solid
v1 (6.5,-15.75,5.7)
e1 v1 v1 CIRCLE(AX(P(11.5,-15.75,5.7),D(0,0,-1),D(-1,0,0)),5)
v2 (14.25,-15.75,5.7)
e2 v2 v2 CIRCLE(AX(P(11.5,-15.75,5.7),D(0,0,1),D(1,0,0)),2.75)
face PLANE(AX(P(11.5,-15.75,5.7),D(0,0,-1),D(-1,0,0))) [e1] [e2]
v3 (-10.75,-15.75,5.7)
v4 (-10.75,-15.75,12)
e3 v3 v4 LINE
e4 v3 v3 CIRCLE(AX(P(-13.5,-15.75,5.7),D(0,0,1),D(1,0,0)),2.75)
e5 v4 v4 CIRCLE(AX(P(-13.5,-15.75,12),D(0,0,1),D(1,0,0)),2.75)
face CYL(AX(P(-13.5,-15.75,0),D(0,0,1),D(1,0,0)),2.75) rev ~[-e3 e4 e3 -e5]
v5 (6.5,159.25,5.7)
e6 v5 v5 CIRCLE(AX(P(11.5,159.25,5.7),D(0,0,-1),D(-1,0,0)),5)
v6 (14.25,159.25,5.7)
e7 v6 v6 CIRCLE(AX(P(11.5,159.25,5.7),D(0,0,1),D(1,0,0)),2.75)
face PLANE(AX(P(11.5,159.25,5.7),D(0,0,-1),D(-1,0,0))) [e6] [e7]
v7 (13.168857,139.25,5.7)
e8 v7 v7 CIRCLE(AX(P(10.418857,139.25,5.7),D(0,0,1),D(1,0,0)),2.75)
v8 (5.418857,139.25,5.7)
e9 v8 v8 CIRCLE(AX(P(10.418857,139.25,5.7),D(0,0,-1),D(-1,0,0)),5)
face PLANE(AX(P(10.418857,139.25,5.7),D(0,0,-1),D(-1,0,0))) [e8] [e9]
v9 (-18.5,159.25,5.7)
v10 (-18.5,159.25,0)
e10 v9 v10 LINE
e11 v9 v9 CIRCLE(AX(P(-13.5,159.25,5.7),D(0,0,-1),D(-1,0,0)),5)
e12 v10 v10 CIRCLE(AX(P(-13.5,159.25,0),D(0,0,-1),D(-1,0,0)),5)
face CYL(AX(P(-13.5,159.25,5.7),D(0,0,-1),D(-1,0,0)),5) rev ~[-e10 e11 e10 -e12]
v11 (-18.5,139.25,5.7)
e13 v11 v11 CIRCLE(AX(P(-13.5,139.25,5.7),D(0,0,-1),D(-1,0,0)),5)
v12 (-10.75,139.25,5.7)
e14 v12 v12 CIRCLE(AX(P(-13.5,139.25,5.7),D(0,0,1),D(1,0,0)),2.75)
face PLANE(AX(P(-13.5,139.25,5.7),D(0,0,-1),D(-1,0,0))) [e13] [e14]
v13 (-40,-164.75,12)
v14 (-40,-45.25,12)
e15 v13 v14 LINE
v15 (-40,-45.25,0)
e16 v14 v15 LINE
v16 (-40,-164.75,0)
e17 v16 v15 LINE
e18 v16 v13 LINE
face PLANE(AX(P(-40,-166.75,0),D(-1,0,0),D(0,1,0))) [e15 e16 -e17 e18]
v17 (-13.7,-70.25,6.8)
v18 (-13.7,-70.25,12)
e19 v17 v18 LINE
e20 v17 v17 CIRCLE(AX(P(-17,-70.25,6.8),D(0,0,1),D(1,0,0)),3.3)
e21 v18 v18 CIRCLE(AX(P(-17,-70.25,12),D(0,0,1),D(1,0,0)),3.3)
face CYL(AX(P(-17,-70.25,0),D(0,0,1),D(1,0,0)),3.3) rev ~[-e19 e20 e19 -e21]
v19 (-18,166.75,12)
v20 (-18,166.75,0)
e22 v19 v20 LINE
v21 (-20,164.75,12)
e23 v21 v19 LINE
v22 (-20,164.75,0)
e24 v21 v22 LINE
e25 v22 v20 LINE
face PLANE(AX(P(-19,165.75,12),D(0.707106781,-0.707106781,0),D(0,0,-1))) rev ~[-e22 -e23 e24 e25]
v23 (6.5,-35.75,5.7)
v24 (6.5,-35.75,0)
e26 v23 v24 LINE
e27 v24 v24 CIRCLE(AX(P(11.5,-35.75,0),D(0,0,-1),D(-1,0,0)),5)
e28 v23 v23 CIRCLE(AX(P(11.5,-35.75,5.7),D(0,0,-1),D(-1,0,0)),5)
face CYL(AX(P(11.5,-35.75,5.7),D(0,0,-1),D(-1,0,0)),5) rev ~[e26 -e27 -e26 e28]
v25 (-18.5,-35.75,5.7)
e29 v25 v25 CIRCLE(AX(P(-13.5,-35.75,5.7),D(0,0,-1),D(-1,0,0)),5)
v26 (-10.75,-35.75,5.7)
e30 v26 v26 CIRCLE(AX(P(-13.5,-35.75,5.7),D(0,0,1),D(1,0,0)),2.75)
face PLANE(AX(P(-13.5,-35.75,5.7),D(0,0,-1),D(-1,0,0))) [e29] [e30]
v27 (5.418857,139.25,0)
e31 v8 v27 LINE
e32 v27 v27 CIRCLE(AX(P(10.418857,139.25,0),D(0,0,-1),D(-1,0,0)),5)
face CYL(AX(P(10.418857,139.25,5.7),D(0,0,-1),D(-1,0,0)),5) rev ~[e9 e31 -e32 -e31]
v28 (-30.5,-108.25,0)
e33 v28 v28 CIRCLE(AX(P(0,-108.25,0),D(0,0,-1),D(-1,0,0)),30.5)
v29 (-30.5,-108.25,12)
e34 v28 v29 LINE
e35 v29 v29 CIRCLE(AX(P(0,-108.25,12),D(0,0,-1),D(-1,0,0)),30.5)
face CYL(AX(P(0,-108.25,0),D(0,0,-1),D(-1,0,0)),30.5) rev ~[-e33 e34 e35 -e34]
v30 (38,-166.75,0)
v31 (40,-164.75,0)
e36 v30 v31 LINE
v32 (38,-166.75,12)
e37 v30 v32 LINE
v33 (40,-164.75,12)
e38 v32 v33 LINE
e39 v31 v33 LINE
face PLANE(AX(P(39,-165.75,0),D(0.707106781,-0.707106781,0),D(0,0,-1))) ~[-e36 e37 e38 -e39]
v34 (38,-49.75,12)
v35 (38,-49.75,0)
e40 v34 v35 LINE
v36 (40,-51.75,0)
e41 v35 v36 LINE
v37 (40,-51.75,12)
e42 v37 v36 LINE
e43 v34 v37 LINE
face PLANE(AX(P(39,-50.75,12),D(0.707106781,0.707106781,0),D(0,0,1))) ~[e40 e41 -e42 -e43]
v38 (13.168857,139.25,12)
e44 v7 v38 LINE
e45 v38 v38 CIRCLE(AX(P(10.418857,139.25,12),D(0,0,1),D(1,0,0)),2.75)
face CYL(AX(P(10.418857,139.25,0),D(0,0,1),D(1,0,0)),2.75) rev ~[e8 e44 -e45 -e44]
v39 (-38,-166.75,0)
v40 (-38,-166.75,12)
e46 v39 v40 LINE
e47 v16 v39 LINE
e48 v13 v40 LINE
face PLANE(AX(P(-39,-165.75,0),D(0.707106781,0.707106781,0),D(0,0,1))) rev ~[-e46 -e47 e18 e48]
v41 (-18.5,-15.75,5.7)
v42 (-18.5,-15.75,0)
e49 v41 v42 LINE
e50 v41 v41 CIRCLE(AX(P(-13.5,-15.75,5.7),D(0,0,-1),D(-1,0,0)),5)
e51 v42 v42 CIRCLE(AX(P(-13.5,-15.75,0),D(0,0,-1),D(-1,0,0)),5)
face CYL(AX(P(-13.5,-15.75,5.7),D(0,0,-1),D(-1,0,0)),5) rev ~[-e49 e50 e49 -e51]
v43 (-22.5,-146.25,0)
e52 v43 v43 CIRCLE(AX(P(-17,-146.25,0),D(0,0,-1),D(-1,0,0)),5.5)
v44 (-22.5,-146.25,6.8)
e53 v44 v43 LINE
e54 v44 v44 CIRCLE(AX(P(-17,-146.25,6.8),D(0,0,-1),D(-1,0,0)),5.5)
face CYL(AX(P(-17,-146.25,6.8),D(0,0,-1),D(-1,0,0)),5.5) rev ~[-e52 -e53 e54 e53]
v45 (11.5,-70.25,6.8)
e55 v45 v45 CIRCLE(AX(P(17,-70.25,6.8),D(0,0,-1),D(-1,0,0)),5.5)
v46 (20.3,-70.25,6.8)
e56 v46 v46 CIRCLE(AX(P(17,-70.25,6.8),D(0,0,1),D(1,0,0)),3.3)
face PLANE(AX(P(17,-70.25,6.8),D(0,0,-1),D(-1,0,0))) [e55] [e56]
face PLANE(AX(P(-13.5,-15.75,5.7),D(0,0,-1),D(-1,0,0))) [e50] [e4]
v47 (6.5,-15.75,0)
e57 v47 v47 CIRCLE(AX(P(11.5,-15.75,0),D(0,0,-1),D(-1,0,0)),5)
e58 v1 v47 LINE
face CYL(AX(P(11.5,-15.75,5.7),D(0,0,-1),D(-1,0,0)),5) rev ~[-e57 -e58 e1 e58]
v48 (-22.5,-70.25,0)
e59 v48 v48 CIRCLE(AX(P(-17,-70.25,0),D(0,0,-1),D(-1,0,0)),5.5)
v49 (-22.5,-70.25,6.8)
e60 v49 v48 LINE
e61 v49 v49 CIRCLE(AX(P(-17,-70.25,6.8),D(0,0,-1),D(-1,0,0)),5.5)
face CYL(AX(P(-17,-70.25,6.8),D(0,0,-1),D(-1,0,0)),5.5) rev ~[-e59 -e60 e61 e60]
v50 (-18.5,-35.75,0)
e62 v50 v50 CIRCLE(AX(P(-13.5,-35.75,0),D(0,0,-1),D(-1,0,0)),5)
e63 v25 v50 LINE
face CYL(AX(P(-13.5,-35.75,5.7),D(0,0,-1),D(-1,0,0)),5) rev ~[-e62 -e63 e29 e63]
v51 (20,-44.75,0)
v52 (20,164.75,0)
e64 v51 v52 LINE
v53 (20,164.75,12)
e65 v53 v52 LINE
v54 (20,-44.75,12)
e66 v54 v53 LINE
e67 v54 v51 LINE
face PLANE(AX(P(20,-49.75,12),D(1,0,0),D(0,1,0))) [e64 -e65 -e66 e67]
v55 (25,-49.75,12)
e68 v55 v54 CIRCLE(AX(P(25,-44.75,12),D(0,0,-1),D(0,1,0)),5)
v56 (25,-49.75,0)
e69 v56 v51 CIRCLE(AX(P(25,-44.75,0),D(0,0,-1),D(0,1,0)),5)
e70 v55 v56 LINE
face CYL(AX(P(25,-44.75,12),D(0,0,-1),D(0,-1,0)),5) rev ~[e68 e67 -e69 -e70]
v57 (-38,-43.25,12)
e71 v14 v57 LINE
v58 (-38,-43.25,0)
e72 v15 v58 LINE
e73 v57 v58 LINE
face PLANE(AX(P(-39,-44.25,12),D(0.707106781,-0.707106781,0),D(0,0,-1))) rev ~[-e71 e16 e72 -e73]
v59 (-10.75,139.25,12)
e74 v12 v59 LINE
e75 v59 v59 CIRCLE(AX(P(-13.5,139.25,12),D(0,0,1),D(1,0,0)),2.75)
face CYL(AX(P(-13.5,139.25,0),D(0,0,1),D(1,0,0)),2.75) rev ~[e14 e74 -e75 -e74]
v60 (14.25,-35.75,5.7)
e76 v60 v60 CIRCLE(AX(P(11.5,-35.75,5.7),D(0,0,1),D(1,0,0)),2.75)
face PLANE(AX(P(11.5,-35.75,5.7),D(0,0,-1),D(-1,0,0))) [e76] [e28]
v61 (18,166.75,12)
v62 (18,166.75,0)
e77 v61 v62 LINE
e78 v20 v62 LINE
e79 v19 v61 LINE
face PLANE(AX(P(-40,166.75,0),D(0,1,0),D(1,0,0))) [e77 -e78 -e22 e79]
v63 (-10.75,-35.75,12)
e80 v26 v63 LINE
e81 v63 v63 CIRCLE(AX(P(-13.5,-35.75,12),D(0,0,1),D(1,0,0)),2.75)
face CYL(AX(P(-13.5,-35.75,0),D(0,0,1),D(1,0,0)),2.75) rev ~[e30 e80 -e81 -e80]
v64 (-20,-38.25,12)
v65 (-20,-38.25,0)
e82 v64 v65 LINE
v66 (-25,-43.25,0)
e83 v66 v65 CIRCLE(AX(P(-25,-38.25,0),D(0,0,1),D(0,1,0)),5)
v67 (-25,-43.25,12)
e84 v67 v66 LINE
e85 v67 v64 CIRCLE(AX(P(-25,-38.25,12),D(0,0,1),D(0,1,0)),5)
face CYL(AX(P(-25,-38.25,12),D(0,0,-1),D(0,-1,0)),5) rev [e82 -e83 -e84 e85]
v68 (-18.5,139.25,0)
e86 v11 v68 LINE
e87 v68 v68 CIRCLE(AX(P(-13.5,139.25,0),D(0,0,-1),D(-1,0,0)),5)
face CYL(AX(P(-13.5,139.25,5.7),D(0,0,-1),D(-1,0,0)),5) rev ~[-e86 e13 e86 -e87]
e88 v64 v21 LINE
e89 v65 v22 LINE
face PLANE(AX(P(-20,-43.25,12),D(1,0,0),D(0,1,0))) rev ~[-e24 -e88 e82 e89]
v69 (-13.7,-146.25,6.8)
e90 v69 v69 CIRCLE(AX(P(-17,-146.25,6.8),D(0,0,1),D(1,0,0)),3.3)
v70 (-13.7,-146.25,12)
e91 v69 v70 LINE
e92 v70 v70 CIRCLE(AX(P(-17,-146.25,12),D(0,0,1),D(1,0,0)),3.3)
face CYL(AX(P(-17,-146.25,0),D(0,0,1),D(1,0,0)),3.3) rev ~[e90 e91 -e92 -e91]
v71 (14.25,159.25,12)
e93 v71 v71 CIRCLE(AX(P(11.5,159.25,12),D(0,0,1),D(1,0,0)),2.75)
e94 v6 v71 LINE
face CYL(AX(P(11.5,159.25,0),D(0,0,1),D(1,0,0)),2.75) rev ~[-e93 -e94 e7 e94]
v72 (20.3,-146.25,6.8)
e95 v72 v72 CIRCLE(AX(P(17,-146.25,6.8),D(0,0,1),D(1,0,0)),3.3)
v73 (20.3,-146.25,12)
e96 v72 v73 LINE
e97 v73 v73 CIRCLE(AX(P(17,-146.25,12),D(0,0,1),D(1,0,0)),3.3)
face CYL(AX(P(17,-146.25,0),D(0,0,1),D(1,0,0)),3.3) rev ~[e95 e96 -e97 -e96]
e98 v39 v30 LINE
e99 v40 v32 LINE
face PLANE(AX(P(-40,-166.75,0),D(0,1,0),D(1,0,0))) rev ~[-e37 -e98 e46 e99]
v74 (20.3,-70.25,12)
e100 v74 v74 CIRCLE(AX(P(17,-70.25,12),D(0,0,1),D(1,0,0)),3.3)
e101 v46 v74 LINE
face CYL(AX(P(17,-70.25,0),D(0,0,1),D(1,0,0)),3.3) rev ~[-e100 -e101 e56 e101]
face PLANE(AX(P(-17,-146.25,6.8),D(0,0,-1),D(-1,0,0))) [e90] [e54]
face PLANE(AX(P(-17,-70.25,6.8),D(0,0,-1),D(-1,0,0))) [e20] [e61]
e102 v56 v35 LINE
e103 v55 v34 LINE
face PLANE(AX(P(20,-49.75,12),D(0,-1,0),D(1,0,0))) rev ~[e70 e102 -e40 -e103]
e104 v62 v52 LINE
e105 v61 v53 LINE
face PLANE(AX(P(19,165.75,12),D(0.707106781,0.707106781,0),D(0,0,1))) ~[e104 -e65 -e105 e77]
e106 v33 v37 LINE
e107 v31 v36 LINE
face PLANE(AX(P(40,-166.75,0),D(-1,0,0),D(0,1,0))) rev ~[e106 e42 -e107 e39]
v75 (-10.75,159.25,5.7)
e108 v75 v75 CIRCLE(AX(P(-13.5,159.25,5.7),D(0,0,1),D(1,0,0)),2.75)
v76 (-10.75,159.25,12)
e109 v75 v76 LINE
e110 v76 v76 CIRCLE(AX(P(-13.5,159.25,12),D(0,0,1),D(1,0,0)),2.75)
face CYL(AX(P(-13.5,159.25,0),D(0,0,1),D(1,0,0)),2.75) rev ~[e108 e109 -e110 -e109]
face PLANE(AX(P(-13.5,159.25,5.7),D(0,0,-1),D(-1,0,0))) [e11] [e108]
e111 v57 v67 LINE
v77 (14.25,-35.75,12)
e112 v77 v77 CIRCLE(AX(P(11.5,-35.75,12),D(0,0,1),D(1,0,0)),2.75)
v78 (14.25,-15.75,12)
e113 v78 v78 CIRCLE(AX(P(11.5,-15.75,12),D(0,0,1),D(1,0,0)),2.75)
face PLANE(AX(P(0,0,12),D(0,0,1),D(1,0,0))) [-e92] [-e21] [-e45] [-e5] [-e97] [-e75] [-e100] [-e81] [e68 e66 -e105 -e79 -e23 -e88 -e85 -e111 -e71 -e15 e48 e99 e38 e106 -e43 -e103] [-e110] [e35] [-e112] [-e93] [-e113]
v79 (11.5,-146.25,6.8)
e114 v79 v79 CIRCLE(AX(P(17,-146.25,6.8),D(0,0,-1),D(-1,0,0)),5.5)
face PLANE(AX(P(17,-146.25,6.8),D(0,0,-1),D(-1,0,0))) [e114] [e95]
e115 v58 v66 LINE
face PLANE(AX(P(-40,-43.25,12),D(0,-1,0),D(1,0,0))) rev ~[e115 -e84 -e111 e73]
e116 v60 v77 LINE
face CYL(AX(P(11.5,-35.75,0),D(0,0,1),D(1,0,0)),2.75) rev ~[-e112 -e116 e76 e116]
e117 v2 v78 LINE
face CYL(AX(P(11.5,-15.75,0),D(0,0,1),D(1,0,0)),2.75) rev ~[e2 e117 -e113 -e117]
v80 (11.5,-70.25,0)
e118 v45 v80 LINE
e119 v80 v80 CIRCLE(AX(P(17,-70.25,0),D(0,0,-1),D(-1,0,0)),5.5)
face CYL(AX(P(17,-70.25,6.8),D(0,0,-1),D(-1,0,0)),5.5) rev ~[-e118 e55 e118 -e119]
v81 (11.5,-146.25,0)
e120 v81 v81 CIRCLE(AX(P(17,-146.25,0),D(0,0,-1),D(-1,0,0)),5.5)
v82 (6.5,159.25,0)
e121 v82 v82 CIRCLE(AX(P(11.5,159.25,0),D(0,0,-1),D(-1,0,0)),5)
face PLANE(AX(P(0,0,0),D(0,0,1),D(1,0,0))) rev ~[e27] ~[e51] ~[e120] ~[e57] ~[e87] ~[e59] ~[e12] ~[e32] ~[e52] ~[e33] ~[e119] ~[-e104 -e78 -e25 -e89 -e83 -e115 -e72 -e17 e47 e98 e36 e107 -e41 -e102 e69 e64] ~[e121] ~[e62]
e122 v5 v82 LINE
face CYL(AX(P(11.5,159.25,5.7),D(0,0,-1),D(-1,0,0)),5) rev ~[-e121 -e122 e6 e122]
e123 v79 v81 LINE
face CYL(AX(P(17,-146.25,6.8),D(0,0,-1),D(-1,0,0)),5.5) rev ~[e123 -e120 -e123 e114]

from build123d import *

# Parameters (mm, degrees)
SKETCH_1_W                   = 80
SKETCH_1_H                   = 333.5
EXTRUDE_1_DEPTH              = 12
CHAMFER_1_SIZE               = 2
HOLE_WIZARD_M5_1_D           = 5.5
HOLE_WIZARD_M5_1_CBORE_D     = 10
HOLE_WIZARD_M5_1_CBORE_DEPTH = 5.7
SKETCH_10_W                  = 20
SKETCH_10_H                  = 210
SKETCH_10_H_2                = 216.5
CUT_EXTRUDE_1_DEPTH          = 172.899861838
CHAMFER_2_SIZE               = 2
FILLET_1_R                   = 5
HOLE_WIZARD_M6_1_D           = 6.6
HOLE_WIZARD_M6_1_CBORE_D     = 11
HOLE_WIZARD_M6_1_CBORE_DEPTH = 6.8
SKETCH_14_R                  = 30.5
CUT_EXTRUDE_2_DEPTH          = 172.899861838


with BuildPart() as part:
    # 草图1 → 凸台-拉伸1 (new body)
    with BuildSketch(Plane.XY):
        Rectangle(SKETCH_1_W, SKETCH_1_H)
    extrude(amount=EXTRUDE_1_DEPTH)

    # 倒角1
    chamfer_1_edges = [part.edges().sort_by_distance(p)[0] for p in [
        (-40, -166.75, 6),
        (40, -166.75, 6),
        (40, 166.75, 6),
        (-40, 166.75, 6),
    ]]
    chamfer(chamfer_1_edges, length=CHAMFER_1_SIZE)

    # M5 六角圆柱头螺钉的柱形沉头孔1 (through all)
    with Locations(Plane(origin=(0, 0, 0), x_dir=(-1, 0, 0), z_dir=(0, 0, -1))):
        with Locations((13.5, -35.75), (13.5, 139.25), (-11.5, 159.25), (-10.418856804, 139.25), (13.5, 159.25), (-11.5, -15.75), (13.5, -15.75), (-11.5, -35.75)):
            CounterBoreHole(HOLE_WIZARD_M5_1_D / 2, HOLE_WIZARD_M5_1_CBORE_D / 2, HOLE_WIZARD_M5_1_CBORE_DEPTH)

    # 草图10 → 切除-拉伸1 (cut, through all)
    with BuildSketch(Plane.XY.offset(12)):
        with Locations((-30, 61.75)):
            Rectangle(SKETCH_10_W, SKETCH_10_H)
        with Locations((30, 58.5)):
            Rectangle(SKETCH_10_W, SKETCH_10_H_2)
    extrude(amount=-CUT_EXTRUDE_1_DEPTH, mode=Mode.SUBTRACT)

    # 倒角2
    chamfer_2_edges = [part.edges().sort_by_distance(p)[0] for p in [
        (-40, -43.25, 6),
        (-20, 166.75, 6),
        (40, -49.75, 6),
        (20, 166.75, 6),
    ]]
    chamfer(chamfer_2_edges, length=CHAMFER_2_SIZE)

    # 圆角1
    fillet_1_edges = [part.edges().sort_by_distance(p)[0] for p in [
        (-20, -43.25, 6),
        (20, -49.75, 6),
    ]]
    fillet(fillet_1_edges, radius=FILLET_1_R)

    # M6 六角圆柱头螺钉的柱形沉头孔1 (through all)
    with Locations(Plane(origin=(0, 0, 0), x_dir=(-1, 0, 0), z_dir=(0, 0, -1))):
        with Locations((-17, -70.25), (-17, -146.25), (17, -146.25), (17, -70.25)):
            CounterBoreHole(HOLE_WIZARD_M6_1_D / 2, HOLE_WIZARD_M6_1_CBORE_D / 2, HOLE_WIZARD_M6_1_CBORE_DEPTH)

    # 草图14 → 切除-拉伸2 (cut, through all)
    with BuildSketch(Plane(origin=(0, 0, 0), x_dir=(-1, 0, 0), z_dir=(0, 0, -1))):
        with Locations((0, -108.25)):
            Circle(SKETCH_14_R)
    extrude(amount=-CUT_EXTRUDE_2_DEPTH, mode=Mode.SUBTRACT)


solid = part.part
